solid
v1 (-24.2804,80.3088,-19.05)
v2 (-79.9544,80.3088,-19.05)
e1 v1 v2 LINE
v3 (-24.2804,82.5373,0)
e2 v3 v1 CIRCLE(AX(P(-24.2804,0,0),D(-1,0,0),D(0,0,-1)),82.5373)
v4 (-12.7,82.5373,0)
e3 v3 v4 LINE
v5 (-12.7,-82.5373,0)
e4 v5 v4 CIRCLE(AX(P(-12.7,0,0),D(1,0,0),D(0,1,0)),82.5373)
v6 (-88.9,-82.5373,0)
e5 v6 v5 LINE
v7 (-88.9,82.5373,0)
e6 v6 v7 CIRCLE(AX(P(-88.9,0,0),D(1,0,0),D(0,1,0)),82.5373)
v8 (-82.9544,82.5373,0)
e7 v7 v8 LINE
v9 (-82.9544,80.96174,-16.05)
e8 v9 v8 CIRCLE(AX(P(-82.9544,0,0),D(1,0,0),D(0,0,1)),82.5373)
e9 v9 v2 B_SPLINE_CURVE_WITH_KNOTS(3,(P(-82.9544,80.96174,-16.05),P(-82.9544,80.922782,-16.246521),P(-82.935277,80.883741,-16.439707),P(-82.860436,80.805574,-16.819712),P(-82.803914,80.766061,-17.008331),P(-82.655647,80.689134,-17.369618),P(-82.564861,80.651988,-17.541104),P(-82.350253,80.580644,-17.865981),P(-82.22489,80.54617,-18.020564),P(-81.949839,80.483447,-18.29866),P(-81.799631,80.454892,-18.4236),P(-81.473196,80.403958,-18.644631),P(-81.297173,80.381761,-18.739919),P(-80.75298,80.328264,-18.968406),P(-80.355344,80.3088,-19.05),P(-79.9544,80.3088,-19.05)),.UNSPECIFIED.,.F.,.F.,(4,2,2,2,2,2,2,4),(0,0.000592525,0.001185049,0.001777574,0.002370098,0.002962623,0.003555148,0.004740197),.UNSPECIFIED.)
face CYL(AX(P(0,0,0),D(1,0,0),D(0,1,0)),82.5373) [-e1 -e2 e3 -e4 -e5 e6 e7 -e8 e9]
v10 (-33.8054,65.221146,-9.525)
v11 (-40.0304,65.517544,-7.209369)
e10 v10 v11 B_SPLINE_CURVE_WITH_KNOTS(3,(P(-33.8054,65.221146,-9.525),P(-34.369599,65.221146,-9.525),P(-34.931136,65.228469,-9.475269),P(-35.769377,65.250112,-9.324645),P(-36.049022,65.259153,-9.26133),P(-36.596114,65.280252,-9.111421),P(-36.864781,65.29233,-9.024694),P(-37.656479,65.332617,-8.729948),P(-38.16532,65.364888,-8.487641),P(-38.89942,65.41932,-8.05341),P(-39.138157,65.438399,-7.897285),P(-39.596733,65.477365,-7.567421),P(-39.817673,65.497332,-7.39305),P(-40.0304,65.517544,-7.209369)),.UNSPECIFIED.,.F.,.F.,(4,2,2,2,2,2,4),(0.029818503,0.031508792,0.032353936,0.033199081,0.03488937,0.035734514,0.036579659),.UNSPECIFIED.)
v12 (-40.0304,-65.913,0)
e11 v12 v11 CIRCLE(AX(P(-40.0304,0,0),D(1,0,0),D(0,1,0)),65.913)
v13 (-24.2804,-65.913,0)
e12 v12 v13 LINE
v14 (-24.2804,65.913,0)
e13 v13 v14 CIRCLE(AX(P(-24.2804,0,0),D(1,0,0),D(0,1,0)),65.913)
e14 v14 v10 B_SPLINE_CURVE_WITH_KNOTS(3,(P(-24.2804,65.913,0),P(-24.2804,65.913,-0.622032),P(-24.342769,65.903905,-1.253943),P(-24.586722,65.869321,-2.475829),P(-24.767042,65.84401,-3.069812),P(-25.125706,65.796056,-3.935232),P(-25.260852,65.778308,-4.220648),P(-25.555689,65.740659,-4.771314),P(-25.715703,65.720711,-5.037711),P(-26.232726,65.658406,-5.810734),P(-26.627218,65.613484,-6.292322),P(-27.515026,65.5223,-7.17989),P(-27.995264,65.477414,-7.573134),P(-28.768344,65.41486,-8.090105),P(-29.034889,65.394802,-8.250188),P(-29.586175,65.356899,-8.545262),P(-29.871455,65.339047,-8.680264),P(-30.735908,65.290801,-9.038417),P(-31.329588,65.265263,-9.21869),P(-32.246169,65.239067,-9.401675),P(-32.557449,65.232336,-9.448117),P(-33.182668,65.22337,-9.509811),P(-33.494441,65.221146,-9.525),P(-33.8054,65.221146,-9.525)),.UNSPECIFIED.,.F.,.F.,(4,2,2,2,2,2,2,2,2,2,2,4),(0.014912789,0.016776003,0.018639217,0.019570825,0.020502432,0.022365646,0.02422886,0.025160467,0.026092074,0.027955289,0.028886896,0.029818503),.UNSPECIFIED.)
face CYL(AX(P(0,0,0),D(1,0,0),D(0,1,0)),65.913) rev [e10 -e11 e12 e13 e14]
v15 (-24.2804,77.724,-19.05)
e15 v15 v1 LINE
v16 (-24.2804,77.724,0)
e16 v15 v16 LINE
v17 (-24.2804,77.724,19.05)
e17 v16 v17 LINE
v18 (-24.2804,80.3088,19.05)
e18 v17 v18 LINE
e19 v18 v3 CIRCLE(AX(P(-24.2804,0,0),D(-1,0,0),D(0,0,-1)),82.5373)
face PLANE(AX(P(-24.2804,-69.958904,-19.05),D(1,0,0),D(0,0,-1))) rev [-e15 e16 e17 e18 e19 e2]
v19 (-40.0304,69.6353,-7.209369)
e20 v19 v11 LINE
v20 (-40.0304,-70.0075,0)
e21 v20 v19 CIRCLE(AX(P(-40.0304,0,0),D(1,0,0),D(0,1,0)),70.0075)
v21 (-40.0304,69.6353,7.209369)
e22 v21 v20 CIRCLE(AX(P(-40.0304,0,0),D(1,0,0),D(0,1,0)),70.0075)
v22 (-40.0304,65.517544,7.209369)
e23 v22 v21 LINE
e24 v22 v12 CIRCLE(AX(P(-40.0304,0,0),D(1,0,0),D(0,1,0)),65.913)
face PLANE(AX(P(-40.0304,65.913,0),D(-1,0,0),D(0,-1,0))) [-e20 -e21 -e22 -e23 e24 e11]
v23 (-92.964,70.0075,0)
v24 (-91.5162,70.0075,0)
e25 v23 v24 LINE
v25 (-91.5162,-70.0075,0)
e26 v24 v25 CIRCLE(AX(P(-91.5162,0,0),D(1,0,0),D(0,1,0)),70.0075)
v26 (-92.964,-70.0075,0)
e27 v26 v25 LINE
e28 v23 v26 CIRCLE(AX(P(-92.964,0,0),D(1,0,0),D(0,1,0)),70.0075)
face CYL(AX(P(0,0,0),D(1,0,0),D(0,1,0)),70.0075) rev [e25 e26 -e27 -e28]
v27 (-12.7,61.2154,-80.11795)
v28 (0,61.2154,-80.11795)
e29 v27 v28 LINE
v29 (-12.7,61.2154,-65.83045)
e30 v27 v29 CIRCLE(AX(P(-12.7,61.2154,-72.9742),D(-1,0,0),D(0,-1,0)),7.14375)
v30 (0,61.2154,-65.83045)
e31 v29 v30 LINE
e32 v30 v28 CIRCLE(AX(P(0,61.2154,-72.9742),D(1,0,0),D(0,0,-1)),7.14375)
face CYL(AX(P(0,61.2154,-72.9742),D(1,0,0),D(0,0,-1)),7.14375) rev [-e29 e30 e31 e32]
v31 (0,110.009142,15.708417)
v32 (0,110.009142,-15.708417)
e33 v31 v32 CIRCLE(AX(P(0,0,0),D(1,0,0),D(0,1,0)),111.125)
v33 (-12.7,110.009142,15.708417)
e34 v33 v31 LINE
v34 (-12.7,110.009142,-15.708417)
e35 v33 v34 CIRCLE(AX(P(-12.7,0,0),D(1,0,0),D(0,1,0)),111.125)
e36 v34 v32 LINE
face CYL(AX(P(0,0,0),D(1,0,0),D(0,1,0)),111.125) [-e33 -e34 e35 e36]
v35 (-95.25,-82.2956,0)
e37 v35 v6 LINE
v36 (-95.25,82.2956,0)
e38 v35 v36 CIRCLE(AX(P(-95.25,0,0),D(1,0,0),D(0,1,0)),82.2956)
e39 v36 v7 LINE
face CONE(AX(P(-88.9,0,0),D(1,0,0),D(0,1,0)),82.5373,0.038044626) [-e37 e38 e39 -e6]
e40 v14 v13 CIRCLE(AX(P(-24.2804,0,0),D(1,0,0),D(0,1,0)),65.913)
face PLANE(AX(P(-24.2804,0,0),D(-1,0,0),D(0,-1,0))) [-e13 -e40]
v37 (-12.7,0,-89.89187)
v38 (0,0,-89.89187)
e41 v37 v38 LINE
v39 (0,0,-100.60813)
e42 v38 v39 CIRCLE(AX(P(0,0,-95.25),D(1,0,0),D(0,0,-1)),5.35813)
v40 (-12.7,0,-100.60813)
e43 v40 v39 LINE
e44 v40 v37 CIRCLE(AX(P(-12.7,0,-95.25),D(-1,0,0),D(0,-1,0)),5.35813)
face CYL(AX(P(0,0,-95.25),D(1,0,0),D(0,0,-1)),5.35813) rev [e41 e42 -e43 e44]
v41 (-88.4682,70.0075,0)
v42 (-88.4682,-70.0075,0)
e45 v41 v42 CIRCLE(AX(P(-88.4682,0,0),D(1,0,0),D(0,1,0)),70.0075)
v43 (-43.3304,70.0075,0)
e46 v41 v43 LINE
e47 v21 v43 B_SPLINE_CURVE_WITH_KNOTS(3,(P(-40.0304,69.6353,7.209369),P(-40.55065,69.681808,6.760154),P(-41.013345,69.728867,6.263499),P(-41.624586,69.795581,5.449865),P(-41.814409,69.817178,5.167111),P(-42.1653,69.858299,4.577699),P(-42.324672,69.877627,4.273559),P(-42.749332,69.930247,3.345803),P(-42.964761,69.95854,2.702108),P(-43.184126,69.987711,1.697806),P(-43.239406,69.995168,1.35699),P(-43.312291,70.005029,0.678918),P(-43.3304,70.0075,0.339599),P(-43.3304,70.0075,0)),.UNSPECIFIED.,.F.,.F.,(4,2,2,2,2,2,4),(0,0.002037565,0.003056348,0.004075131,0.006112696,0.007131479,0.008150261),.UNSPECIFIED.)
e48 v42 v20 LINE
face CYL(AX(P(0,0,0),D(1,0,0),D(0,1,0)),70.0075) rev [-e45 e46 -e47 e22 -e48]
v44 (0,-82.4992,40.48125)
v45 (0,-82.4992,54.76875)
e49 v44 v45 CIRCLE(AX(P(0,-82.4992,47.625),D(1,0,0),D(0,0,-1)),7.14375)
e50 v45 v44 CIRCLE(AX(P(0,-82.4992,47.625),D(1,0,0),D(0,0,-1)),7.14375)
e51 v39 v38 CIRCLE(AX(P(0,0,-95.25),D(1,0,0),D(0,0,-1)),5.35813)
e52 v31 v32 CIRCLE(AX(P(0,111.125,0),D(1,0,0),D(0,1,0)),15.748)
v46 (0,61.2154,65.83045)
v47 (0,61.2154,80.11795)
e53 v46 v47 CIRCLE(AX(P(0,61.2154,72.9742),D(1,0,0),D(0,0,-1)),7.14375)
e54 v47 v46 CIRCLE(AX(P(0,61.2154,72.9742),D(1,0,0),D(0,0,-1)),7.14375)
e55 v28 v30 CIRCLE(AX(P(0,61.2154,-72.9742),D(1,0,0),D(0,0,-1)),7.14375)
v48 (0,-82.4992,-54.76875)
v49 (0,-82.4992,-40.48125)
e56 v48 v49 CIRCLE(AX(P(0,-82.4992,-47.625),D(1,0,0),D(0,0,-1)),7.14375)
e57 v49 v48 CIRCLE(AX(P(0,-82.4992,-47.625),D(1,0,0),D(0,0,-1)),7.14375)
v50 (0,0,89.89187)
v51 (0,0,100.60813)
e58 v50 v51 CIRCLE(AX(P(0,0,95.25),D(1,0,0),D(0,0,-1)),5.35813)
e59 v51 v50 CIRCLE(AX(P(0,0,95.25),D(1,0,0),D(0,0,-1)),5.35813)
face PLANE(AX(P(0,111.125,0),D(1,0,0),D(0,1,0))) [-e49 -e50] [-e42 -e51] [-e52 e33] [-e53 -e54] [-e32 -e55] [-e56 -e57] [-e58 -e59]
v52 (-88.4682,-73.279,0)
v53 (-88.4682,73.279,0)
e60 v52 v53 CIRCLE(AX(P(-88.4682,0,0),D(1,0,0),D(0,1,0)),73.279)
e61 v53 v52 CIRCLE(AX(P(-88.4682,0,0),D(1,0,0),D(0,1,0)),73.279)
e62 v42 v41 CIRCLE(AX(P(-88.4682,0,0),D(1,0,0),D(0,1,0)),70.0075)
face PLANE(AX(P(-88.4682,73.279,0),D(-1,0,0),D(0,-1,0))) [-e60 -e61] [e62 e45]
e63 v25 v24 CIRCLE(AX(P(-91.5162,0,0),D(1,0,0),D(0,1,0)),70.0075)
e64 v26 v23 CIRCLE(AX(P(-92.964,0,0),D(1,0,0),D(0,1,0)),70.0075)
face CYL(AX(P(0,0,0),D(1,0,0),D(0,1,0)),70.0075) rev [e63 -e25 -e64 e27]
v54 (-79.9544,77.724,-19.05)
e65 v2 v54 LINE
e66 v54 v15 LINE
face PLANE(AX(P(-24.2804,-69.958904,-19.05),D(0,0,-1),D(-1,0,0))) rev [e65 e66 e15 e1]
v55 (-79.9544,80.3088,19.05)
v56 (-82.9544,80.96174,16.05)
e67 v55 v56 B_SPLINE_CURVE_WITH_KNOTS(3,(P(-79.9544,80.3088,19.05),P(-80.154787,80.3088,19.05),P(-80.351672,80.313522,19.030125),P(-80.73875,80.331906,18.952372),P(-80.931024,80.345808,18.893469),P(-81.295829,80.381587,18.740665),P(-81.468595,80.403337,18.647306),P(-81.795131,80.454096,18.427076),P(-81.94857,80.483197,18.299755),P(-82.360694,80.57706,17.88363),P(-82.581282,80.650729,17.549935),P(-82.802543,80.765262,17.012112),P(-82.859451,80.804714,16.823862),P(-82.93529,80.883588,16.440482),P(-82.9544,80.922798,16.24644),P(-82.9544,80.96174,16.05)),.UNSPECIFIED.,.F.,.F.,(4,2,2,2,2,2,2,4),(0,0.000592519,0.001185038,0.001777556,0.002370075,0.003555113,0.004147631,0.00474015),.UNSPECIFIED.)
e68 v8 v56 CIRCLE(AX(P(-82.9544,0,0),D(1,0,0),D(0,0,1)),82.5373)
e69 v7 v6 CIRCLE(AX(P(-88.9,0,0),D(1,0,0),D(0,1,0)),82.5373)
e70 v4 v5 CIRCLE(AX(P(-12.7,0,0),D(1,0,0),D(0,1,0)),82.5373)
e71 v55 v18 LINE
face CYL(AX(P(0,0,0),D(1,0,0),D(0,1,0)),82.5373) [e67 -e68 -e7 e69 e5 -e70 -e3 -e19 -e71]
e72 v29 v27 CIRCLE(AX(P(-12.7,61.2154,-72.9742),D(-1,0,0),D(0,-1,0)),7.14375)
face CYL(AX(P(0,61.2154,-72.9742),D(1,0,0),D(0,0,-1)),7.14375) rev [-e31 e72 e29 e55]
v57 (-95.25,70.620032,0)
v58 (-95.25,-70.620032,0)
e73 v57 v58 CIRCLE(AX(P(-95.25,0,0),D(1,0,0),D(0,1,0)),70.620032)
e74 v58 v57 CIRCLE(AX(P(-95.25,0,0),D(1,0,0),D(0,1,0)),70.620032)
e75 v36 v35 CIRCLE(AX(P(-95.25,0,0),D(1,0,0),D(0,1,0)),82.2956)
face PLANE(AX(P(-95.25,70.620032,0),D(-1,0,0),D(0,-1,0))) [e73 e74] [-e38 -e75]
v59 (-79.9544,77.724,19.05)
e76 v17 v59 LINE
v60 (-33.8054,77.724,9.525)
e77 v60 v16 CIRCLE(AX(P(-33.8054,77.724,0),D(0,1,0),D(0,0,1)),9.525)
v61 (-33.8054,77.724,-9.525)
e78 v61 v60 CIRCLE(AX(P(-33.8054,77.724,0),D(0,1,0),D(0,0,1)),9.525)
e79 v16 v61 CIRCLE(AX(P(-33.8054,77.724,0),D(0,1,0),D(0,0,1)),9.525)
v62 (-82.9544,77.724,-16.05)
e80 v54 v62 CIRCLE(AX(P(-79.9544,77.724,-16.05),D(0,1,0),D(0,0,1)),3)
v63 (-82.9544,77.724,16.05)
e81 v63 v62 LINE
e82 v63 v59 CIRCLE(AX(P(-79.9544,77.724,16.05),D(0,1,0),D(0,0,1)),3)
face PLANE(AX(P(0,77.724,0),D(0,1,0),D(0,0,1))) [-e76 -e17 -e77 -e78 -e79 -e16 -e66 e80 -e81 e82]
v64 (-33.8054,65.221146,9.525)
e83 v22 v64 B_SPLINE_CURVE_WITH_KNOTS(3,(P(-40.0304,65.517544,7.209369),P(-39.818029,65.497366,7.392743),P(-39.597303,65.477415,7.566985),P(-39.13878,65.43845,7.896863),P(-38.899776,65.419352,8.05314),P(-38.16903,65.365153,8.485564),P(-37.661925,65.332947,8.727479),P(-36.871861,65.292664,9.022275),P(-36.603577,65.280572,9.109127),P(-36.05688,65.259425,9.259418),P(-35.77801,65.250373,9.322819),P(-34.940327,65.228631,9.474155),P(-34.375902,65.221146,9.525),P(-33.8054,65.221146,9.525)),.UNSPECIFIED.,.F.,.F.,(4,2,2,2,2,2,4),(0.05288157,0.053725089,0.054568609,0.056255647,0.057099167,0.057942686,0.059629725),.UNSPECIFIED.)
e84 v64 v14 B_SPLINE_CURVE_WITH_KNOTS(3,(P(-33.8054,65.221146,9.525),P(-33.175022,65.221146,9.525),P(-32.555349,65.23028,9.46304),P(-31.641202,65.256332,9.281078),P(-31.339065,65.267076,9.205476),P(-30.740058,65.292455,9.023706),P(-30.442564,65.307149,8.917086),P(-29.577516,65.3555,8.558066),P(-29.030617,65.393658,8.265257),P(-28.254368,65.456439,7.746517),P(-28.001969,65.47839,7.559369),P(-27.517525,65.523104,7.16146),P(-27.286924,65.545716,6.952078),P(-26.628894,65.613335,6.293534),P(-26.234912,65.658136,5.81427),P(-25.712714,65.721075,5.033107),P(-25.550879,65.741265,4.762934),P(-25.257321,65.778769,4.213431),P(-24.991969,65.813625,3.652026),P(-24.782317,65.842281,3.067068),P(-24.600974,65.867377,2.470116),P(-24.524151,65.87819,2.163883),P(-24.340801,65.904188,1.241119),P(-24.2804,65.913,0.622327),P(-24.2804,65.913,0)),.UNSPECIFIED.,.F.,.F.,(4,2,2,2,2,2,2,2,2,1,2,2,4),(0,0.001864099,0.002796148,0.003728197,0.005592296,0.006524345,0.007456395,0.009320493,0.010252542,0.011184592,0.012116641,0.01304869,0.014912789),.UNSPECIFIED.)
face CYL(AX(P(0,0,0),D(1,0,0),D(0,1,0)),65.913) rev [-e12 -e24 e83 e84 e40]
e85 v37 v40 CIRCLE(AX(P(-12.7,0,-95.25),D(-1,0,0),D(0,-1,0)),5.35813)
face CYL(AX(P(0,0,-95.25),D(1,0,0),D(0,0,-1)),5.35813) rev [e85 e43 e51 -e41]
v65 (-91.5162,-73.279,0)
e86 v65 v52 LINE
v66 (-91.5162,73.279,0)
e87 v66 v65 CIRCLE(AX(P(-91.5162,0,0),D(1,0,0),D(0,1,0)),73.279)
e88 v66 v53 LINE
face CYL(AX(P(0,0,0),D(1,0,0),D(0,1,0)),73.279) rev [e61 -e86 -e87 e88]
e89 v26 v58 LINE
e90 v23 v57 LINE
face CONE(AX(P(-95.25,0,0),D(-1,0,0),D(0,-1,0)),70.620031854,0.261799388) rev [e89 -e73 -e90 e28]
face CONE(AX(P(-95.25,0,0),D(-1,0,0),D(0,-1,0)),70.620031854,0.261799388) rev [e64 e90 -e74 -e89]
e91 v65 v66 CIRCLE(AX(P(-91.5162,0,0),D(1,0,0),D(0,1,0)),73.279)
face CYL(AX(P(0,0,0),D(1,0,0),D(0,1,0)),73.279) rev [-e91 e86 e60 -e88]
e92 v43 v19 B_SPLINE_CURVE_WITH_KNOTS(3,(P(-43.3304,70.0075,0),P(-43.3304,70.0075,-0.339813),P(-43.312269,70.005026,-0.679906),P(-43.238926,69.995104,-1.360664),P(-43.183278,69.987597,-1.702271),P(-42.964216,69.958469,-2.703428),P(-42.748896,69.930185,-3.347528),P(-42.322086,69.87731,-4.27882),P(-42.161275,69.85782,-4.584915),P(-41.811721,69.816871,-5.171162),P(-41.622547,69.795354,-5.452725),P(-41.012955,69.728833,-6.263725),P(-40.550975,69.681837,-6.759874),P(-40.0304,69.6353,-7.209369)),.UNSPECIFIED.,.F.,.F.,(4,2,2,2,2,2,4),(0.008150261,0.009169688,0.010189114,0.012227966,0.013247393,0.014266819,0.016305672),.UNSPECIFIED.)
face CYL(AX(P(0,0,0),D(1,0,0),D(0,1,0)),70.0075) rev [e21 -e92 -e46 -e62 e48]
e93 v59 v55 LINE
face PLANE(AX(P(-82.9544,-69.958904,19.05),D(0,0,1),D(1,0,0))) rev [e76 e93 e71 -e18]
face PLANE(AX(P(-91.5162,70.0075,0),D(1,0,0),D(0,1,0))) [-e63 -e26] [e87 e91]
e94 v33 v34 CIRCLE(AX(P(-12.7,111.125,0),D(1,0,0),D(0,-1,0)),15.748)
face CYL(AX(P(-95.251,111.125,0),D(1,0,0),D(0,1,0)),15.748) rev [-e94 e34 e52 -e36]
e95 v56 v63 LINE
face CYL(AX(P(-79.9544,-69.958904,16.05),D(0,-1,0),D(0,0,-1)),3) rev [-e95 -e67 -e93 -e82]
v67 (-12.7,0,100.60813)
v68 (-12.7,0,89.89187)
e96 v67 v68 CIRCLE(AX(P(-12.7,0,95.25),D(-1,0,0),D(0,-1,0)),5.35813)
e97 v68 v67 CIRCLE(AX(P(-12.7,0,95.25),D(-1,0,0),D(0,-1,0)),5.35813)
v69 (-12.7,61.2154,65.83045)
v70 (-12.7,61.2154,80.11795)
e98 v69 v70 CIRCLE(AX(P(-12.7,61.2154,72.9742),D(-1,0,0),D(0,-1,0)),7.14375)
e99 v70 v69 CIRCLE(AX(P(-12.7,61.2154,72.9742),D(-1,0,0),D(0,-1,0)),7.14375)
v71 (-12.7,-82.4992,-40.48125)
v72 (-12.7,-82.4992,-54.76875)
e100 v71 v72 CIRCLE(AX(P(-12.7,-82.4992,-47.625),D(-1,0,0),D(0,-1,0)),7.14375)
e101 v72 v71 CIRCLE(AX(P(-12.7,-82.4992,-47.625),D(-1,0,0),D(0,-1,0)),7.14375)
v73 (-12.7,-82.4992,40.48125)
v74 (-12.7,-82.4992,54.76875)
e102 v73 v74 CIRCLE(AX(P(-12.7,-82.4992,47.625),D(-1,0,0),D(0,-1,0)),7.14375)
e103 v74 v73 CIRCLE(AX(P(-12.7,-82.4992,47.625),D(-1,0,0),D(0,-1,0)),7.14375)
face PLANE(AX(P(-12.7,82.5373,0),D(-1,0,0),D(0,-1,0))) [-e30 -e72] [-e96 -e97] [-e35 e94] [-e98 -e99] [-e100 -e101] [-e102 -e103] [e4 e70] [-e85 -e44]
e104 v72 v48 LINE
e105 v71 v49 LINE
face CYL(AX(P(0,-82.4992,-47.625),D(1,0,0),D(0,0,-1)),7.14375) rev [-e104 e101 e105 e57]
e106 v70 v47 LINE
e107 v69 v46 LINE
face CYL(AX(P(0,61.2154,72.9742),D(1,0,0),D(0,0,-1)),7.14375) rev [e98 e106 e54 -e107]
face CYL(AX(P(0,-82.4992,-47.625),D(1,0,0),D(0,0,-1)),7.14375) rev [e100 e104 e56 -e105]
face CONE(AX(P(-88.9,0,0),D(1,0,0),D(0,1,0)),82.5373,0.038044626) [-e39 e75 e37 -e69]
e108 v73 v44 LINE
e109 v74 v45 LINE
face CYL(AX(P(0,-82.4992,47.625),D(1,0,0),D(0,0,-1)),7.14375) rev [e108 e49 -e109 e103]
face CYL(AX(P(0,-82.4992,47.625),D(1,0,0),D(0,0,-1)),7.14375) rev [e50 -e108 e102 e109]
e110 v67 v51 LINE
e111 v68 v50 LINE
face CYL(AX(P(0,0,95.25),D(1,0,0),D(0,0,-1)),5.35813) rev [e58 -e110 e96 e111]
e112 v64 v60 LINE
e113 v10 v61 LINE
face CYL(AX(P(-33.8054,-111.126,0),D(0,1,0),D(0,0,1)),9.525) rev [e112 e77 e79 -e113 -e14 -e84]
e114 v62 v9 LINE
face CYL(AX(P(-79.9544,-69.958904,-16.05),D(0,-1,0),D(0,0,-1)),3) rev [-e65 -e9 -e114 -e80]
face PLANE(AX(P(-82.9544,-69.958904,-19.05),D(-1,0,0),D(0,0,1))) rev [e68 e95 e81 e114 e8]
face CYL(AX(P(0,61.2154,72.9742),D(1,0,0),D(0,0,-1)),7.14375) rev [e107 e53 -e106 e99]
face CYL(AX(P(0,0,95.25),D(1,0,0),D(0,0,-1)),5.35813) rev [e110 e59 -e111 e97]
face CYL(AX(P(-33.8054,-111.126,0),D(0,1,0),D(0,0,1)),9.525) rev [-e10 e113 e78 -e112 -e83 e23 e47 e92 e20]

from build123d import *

# Parameters (mm, degrees)
F_9_16_0_5625_DIAMETER_HOLE1_D = 14.2875
F_1_2_13_TAPPED_HOLE1_D        = 10.71626
EXTRUDE1_START                 = 77.724
SKETCH8_W                      = 58.674
SKETCH8_H                      = 38.1
EXTRUDE1_DEPTH                 = 4.8133
EXTRUDE2_REACH                 = 240.925
EXTRUDE2_END_RADIUS            = 65.913
SKETCH9_R                      = 9.525
FILLET1_R                      = 3
EXTRUDE3_REACH                 = 185.766


with BuildPart() as part:
    # Sketch1 → Revolve1 (revolve)
    with BuildSketch(Plane.XY):
        Polygon((-95.25, 70.620031854), (-95.25, 82.2956), (-88.9, 82.5373), (-12.7, 82.5373), (-12.7, 111.125), (0, 111.125), (0, 0), (-24.2804, 0), (-24.2804, 65.913), (-40.0304, 65.913), (-40.0304, 70.0075), (-88.4682, 70.0075), (-88.4682, 73.279), (-91.5162, 73.279), (-91.5162, 70.0075), (-92.964, 70.0075), align=None)
    revolve(axis=Axis((0, 0, 0), (-1, 0, 0)))

    # 9/16 (0.5625) Diameter Hole1 (through all)
    with Locations(Plane(origin=(0, 0, 0), x_dir=(0, 0, -1), z_dir=(1, 0, 0))):
        with Locations((-72.9742, 61.2154), (72.9742, 61.2154), (-47.625, -82.4992), (47.625, -82.4992)):
            Hole(F_9_16_0_5625_DIAMETER_HOLE1_D / 2)

    # 1/2-13 Tapped Hole1 (through all)
    with Locations(Plane(origin=(0, 0, 0), x_dir=(0, 0, -1), z_dir=(1, 0, 0))):
        with Locations((-95.25, 0), (95.25, 0)):
            Hole(F_1_2_13_TAPPED_HOLE1_D / 2)

    # Sketch8 → Extrude1 (cut)
    with BuildSketch(Plane(origin=(0, 0, 0), x_dir=(1, 0, 0), z_dir=(0, 1, 0)).offset(EXTRUDE1_START)):
        with Locations((-53.6174, 0)):
            Rectangle(SKETCH8_W, SKETCH8_H)
    extrude(amount=EXTRUDE1_DEPTH, mode=Mode.SUBTRACT)

    # Extrude2: up to this cylinder (the profile starts outside it)
    extrude2_end = Plane(origin=(-33.8054, 0, 0), z_dir=(1, 0, 0)) * Cylinder(EXTRUDE2_END_RADIUS, 614.676, mode=Mode.PRIVATE)
    # Sketch9 → Extrude2 (cut, up to the surface)
    with BuildSketch(Plane(origin=(0, 77.724, 0), x_dir=(1, 0, 0), z_dir=(0, 1, 0)), mode=Mode.PRIVATE) as extrude2_sk1:
        with Locations((-33.8054, 0)):
            Circle(SKETCH9_R)
    extrude2_tool1 = extrude(extrude2_sk1.sketch, amount=-EXTRUDE2_REACH, mode=Mode.PRIVATE) - extrude2_end
    add(extrude2_tool1.solids().sort_by_distance((-33.8054, 77.724, 0))[0], mode=Mode.SUBTRACT)

    # Fillet1
    fillet1_edges = [part.edges().sort_by_distance(p)[0] for p in [
        (-82.9544, 79.016400105, 19.05),
        (-82.9544, 79.016400105, -19.05),
    ]]
    fillet(fillet1_edges, radius=FILLET1_R)

    # Sketch10 → Extrude3 (cut, up to next)
    with BuildSketch(Plane(origin=(0, 0, 0), x_dir=(0, 0, -1), z_dir=(1, 0, 0)), mode=Mode.PRIVATE) as extrude3_sk1:
        with BuildLine():
            ThreePointArc((-15.708416989, 110.009141714), (0, 95.377), (15.708416989, 110.009141714))
            ThreePointArc((15.708416989, 110.009141714), (0, 111.125), (-15.708416989, 110.009141714))
        make_face()
    extrude3_tool1 = extrude(extrude3_sk1.sketch, amount=-EXTRUDE3_REACH, mode=Mode.PRIVATE) & part.part
    add(extrude3_tool1.solids().sort_by_distance((0, 104.244395, 0))[0], mode=Mode.SUBTRACT)


solid = part.part
